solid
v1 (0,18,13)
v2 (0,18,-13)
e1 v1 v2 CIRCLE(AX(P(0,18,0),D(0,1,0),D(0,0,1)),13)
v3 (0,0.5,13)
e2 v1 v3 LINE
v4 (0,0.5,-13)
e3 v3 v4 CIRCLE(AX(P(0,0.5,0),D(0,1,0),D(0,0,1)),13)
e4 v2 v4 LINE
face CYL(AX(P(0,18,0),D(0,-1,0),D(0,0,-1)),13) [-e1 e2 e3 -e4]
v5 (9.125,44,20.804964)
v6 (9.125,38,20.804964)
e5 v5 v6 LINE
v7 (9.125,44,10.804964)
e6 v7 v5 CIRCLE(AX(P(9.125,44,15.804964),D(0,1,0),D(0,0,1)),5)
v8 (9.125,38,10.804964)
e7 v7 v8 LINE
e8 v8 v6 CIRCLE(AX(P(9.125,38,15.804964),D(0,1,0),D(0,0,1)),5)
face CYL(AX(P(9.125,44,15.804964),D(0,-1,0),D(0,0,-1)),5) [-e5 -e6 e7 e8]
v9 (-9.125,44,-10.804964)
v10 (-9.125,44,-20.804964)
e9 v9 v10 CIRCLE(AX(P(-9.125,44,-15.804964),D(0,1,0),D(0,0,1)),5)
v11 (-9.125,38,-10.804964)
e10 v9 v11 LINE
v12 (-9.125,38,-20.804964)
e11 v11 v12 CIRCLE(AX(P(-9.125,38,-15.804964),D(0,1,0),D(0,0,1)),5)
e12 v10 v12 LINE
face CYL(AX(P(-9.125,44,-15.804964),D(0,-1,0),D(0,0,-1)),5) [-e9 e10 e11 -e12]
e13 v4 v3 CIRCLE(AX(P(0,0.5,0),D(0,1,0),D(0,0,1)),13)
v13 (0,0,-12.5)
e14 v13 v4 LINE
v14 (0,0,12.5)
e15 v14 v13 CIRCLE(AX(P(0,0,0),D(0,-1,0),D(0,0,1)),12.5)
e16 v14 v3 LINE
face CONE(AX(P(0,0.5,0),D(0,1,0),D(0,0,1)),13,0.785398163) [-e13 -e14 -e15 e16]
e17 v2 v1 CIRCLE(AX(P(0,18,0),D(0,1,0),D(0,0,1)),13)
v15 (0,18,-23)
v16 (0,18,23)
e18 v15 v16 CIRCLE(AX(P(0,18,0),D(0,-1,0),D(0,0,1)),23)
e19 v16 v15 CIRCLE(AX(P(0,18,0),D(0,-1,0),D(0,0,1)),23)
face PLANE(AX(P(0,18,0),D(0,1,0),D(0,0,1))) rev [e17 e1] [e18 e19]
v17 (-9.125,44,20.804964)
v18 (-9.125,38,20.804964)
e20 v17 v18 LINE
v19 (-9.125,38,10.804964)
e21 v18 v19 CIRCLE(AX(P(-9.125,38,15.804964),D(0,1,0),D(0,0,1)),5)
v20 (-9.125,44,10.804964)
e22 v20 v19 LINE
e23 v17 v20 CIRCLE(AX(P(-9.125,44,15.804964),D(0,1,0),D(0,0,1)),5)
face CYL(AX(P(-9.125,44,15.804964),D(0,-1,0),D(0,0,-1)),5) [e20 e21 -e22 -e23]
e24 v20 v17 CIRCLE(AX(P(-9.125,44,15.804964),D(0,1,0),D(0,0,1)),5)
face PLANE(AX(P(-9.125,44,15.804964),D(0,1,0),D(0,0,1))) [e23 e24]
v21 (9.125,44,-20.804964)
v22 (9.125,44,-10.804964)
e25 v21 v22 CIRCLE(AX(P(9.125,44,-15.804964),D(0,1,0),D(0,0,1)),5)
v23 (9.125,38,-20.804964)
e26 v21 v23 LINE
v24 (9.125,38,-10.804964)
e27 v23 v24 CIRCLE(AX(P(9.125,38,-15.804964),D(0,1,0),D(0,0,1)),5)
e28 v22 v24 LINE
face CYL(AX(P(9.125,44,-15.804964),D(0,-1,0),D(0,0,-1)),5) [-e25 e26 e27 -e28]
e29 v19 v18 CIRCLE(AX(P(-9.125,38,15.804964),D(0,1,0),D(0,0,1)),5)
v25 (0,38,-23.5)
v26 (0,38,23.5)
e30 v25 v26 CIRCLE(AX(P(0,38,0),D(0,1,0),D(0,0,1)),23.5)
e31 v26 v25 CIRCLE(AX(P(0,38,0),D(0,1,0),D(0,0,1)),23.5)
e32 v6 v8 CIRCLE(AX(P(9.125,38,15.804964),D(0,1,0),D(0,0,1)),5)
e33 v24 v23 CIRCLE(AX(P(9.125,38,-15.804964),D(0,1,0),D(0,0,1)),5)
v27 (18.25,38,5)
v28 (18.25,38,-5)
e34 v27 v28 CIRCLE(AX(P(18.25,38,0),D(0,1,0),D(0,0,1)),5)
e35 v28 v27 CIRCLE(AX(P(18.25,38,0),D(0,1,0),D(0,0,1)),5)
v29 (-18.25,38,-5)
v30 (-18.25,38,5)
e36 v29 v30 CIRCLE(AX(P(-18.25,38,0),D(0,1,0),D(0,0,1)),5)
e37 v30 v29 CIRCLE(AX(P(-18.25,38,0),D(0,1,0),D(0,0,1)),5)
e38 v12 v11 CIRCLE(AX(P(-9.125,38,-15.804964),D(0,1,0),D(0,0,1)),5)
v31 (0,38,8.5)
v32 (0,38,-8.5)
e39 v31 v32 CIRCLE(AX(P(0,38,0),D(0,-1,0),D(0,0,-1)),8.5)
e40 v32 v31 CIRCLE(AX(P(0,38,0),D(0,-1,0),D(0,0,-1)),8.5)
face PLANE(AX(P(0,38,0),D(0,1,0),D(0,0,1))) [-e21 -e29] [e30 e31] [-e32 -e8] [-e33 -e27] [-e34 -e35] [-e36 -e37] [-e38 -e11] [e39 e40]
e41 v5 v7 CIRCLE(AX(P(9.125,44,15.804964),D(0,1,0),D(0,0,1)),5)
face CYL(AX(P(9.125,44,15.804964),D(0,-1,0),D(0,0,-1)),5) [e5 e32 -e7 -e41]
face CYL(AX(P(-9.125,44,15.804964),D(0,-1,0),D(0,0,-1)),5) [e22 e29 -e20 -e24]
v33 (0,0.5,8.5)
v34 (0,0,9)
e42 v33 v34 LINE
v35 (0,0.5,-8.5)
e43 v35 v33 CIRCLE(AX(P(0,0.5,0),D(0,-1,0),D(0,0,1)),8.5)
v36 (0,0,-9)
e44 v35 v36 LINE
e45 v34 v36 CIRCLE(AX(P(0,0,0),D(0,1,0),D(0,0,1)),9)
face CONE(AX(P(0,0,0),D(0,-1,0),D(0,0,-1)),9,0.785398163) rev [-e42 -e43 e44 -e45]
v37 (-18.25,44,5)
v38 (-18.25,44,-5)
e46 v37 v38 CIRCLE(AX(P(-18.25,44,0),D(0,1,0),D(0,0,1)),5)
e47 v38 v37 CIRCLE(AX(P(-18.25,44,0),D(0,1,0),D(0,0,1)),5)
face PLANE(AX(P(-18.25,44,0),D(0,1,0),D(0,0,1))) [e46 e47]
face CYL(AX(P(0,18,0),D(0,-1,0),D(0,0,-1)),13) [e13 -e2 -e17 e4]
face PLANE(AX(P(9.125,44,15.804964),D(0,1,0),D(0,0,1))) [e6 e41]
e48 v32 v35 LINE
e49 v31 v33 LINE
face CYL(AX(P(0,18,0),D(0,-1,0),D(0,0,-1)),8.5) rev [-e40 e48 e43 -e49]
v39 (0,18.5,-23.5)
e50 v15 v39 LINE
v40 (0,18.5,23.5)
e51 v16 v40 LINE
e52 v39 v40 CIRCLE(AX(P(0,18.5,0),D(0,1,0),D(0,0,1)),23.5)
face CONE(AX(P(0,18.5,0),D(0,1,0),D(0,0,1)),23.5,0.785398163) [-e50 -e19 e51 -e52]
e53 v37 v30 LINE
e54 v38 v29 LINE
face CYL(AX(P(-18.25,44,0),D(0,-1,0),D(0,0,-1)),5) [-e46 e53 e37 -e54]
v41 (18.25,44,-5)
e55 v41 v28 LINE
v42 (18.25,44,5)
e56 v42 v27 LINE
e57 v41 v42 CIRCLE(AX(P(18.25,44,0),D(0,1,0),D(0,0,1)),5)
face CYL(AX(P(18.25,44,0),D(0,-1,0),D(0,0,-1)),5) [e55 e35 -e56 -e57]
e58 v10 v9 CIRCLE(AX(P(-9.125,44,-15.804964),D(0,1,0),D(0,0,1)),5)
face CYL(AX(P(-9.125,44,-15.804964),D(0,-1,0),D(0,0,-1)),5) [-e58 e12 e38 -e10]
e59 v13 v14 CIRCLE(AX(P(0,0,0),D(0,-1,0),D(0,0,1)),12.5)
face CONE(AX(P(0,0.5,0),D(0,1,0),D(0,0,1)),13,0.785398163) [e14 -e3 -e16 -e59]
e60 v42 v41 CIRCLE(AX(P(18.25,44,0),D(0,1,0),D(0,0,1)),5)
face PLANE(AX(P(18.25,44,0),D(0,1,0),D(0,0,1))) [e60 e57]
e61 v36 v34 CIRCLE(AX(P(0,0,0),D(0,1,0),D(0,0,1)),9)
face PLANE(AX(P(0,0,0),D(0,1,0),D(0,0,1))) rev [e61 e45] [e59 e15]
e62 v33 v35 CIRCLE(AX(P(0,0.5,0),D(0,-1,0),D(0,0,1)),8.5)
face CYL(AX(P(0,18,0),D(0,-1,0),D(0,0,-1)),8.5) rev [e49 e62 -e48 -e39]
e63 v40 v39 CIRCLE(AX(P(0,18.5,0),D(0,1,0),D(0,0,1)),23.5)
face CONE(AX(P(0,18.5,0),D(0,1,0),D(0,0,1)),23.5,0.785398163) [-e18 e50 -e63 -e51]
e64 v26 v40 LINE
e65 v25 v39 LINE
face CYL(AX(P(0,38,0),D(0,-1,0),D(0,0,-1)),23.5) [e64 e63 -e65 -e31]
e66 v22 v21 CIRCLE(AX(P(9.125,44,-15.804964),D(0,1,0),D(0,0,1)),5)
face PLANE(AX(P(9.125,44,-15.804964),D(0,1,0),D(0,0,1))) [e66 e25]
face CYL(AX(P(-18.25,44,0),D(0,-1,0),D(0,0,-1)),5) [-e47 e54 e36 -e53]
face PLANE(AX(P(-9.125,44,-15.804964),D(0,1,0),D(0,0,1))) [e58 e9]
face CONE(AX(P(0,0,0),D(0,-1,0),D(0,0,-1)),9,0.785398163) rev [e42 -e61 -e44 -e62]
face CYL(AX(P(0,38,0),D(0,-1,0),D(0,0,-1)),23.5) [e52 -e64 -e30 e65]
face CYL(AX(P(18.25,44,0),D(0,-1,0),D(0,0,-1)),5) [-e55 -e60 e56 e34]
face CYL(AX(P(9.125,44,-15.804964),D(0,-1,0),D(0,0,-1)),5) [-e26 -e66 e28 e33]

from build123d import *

# Parameters (mm, degrees)
SKETCH_1_R          = 13
SKETCH_1_R_2        = 8.5
EXTRUDE_1_DEPTH     = 18
SKETCH_2_R          = 23.5
EXTRUDE_2_DEPTH     = 20
SKETCH_3_R          = 8.5
CUT_EXTRUDE_1_DEPTH = 39.787884706
SKETCH_4_R          = 5
EXTRUDE_3_DEPTH     = 6
CHAMFER_1_SIZE      = 0.5


with BuildPart() as part:
    # 草图1 → 拉伸1 (new body)
    with BuildSketch(Plane(origin=(0, 0, 0), x_dir=(1, 0, 0), z_dir=(0, 1, 0))):
        with Locations(Location((0, 0, 0), (0, 0, 270))):
            Circle(SKETCH_1_R)
        with Locations(Location((0, 0, 0), (0, 0, 270))):
            Circle(SKETCH_1_R_2, mode=Mode.SUBTRACT)
    extrude(amount=EXTRUDE_1_DEPTH)

    # 草图2 → 拉伸2 (add)
    with BuildSketch(Plane(origin=(0, 18, 0), x_dir=(-1, 0, 0), z_dir=(0, 1, 0))):
        with Locations(Location((0, 0, 0), (0, 0, 90))):
            Circle(SKETCH_2_R)
    extrude(amount=EXTRUDE_2_DEPTH)

    # 草图3 → 切除-拉伸1 (cut, through all)
    with BuildSketch(Plane.XZ.offset(-18)):
        with Locations(Location((0, 0, 0), (0, 0, 270))):
            Circle(SKETCH_3_R)
    extrude(amount=-CUT_EXTRUDE_1_DEPTH, mode=Mode.SUBTRACT)

    # 草图4 → 拉伸3 (add)
    with BuildSketch(Plane(origin=(0, 38, 0), x_dir=(-1, 0, 0), z_dir=(0, 1, 0))):
        with Locations(Location((-18.25, 0, 0), (0, 0, 90))):
            Circle(SKETCH_4_R)
        with Locations(Location((-9.125, 15.804963619, 0), (0, 0, 90))):
            Circle(SKETCH_4_R)
        with Locations(Location((9.125, 15.804963619, 0), (0, 0, 90))):
            Circle(SKETCH_4_R)
        with Locations(Location((18.25, 0, 0), (0, 0, 90))):
            Circle(SKETCH_4_R)
        with Locations(Location((9.125, -15.804963619, 0), (0, 0, 90))):
            Circle(SKETCH_4_R)
        with Locations(Location((-9.125, -15.804963619, 0), (0, 0, 90))):
            Circle(SKETCH_4_R)
    extrude(amount=EXTRUDE_3_DEPTH)

    # 倒角1
    chamfer_1_edges = [part.edges().sort_by_distance(p)[0] for p in [
        (0, 0, -13),
        (0, 0, -8.5),
        (0, 18, -23.5),
    ]]
    chamfer(chamfer_1_edges, length=CHAMFER_1_SIZE)


solid = part.part
